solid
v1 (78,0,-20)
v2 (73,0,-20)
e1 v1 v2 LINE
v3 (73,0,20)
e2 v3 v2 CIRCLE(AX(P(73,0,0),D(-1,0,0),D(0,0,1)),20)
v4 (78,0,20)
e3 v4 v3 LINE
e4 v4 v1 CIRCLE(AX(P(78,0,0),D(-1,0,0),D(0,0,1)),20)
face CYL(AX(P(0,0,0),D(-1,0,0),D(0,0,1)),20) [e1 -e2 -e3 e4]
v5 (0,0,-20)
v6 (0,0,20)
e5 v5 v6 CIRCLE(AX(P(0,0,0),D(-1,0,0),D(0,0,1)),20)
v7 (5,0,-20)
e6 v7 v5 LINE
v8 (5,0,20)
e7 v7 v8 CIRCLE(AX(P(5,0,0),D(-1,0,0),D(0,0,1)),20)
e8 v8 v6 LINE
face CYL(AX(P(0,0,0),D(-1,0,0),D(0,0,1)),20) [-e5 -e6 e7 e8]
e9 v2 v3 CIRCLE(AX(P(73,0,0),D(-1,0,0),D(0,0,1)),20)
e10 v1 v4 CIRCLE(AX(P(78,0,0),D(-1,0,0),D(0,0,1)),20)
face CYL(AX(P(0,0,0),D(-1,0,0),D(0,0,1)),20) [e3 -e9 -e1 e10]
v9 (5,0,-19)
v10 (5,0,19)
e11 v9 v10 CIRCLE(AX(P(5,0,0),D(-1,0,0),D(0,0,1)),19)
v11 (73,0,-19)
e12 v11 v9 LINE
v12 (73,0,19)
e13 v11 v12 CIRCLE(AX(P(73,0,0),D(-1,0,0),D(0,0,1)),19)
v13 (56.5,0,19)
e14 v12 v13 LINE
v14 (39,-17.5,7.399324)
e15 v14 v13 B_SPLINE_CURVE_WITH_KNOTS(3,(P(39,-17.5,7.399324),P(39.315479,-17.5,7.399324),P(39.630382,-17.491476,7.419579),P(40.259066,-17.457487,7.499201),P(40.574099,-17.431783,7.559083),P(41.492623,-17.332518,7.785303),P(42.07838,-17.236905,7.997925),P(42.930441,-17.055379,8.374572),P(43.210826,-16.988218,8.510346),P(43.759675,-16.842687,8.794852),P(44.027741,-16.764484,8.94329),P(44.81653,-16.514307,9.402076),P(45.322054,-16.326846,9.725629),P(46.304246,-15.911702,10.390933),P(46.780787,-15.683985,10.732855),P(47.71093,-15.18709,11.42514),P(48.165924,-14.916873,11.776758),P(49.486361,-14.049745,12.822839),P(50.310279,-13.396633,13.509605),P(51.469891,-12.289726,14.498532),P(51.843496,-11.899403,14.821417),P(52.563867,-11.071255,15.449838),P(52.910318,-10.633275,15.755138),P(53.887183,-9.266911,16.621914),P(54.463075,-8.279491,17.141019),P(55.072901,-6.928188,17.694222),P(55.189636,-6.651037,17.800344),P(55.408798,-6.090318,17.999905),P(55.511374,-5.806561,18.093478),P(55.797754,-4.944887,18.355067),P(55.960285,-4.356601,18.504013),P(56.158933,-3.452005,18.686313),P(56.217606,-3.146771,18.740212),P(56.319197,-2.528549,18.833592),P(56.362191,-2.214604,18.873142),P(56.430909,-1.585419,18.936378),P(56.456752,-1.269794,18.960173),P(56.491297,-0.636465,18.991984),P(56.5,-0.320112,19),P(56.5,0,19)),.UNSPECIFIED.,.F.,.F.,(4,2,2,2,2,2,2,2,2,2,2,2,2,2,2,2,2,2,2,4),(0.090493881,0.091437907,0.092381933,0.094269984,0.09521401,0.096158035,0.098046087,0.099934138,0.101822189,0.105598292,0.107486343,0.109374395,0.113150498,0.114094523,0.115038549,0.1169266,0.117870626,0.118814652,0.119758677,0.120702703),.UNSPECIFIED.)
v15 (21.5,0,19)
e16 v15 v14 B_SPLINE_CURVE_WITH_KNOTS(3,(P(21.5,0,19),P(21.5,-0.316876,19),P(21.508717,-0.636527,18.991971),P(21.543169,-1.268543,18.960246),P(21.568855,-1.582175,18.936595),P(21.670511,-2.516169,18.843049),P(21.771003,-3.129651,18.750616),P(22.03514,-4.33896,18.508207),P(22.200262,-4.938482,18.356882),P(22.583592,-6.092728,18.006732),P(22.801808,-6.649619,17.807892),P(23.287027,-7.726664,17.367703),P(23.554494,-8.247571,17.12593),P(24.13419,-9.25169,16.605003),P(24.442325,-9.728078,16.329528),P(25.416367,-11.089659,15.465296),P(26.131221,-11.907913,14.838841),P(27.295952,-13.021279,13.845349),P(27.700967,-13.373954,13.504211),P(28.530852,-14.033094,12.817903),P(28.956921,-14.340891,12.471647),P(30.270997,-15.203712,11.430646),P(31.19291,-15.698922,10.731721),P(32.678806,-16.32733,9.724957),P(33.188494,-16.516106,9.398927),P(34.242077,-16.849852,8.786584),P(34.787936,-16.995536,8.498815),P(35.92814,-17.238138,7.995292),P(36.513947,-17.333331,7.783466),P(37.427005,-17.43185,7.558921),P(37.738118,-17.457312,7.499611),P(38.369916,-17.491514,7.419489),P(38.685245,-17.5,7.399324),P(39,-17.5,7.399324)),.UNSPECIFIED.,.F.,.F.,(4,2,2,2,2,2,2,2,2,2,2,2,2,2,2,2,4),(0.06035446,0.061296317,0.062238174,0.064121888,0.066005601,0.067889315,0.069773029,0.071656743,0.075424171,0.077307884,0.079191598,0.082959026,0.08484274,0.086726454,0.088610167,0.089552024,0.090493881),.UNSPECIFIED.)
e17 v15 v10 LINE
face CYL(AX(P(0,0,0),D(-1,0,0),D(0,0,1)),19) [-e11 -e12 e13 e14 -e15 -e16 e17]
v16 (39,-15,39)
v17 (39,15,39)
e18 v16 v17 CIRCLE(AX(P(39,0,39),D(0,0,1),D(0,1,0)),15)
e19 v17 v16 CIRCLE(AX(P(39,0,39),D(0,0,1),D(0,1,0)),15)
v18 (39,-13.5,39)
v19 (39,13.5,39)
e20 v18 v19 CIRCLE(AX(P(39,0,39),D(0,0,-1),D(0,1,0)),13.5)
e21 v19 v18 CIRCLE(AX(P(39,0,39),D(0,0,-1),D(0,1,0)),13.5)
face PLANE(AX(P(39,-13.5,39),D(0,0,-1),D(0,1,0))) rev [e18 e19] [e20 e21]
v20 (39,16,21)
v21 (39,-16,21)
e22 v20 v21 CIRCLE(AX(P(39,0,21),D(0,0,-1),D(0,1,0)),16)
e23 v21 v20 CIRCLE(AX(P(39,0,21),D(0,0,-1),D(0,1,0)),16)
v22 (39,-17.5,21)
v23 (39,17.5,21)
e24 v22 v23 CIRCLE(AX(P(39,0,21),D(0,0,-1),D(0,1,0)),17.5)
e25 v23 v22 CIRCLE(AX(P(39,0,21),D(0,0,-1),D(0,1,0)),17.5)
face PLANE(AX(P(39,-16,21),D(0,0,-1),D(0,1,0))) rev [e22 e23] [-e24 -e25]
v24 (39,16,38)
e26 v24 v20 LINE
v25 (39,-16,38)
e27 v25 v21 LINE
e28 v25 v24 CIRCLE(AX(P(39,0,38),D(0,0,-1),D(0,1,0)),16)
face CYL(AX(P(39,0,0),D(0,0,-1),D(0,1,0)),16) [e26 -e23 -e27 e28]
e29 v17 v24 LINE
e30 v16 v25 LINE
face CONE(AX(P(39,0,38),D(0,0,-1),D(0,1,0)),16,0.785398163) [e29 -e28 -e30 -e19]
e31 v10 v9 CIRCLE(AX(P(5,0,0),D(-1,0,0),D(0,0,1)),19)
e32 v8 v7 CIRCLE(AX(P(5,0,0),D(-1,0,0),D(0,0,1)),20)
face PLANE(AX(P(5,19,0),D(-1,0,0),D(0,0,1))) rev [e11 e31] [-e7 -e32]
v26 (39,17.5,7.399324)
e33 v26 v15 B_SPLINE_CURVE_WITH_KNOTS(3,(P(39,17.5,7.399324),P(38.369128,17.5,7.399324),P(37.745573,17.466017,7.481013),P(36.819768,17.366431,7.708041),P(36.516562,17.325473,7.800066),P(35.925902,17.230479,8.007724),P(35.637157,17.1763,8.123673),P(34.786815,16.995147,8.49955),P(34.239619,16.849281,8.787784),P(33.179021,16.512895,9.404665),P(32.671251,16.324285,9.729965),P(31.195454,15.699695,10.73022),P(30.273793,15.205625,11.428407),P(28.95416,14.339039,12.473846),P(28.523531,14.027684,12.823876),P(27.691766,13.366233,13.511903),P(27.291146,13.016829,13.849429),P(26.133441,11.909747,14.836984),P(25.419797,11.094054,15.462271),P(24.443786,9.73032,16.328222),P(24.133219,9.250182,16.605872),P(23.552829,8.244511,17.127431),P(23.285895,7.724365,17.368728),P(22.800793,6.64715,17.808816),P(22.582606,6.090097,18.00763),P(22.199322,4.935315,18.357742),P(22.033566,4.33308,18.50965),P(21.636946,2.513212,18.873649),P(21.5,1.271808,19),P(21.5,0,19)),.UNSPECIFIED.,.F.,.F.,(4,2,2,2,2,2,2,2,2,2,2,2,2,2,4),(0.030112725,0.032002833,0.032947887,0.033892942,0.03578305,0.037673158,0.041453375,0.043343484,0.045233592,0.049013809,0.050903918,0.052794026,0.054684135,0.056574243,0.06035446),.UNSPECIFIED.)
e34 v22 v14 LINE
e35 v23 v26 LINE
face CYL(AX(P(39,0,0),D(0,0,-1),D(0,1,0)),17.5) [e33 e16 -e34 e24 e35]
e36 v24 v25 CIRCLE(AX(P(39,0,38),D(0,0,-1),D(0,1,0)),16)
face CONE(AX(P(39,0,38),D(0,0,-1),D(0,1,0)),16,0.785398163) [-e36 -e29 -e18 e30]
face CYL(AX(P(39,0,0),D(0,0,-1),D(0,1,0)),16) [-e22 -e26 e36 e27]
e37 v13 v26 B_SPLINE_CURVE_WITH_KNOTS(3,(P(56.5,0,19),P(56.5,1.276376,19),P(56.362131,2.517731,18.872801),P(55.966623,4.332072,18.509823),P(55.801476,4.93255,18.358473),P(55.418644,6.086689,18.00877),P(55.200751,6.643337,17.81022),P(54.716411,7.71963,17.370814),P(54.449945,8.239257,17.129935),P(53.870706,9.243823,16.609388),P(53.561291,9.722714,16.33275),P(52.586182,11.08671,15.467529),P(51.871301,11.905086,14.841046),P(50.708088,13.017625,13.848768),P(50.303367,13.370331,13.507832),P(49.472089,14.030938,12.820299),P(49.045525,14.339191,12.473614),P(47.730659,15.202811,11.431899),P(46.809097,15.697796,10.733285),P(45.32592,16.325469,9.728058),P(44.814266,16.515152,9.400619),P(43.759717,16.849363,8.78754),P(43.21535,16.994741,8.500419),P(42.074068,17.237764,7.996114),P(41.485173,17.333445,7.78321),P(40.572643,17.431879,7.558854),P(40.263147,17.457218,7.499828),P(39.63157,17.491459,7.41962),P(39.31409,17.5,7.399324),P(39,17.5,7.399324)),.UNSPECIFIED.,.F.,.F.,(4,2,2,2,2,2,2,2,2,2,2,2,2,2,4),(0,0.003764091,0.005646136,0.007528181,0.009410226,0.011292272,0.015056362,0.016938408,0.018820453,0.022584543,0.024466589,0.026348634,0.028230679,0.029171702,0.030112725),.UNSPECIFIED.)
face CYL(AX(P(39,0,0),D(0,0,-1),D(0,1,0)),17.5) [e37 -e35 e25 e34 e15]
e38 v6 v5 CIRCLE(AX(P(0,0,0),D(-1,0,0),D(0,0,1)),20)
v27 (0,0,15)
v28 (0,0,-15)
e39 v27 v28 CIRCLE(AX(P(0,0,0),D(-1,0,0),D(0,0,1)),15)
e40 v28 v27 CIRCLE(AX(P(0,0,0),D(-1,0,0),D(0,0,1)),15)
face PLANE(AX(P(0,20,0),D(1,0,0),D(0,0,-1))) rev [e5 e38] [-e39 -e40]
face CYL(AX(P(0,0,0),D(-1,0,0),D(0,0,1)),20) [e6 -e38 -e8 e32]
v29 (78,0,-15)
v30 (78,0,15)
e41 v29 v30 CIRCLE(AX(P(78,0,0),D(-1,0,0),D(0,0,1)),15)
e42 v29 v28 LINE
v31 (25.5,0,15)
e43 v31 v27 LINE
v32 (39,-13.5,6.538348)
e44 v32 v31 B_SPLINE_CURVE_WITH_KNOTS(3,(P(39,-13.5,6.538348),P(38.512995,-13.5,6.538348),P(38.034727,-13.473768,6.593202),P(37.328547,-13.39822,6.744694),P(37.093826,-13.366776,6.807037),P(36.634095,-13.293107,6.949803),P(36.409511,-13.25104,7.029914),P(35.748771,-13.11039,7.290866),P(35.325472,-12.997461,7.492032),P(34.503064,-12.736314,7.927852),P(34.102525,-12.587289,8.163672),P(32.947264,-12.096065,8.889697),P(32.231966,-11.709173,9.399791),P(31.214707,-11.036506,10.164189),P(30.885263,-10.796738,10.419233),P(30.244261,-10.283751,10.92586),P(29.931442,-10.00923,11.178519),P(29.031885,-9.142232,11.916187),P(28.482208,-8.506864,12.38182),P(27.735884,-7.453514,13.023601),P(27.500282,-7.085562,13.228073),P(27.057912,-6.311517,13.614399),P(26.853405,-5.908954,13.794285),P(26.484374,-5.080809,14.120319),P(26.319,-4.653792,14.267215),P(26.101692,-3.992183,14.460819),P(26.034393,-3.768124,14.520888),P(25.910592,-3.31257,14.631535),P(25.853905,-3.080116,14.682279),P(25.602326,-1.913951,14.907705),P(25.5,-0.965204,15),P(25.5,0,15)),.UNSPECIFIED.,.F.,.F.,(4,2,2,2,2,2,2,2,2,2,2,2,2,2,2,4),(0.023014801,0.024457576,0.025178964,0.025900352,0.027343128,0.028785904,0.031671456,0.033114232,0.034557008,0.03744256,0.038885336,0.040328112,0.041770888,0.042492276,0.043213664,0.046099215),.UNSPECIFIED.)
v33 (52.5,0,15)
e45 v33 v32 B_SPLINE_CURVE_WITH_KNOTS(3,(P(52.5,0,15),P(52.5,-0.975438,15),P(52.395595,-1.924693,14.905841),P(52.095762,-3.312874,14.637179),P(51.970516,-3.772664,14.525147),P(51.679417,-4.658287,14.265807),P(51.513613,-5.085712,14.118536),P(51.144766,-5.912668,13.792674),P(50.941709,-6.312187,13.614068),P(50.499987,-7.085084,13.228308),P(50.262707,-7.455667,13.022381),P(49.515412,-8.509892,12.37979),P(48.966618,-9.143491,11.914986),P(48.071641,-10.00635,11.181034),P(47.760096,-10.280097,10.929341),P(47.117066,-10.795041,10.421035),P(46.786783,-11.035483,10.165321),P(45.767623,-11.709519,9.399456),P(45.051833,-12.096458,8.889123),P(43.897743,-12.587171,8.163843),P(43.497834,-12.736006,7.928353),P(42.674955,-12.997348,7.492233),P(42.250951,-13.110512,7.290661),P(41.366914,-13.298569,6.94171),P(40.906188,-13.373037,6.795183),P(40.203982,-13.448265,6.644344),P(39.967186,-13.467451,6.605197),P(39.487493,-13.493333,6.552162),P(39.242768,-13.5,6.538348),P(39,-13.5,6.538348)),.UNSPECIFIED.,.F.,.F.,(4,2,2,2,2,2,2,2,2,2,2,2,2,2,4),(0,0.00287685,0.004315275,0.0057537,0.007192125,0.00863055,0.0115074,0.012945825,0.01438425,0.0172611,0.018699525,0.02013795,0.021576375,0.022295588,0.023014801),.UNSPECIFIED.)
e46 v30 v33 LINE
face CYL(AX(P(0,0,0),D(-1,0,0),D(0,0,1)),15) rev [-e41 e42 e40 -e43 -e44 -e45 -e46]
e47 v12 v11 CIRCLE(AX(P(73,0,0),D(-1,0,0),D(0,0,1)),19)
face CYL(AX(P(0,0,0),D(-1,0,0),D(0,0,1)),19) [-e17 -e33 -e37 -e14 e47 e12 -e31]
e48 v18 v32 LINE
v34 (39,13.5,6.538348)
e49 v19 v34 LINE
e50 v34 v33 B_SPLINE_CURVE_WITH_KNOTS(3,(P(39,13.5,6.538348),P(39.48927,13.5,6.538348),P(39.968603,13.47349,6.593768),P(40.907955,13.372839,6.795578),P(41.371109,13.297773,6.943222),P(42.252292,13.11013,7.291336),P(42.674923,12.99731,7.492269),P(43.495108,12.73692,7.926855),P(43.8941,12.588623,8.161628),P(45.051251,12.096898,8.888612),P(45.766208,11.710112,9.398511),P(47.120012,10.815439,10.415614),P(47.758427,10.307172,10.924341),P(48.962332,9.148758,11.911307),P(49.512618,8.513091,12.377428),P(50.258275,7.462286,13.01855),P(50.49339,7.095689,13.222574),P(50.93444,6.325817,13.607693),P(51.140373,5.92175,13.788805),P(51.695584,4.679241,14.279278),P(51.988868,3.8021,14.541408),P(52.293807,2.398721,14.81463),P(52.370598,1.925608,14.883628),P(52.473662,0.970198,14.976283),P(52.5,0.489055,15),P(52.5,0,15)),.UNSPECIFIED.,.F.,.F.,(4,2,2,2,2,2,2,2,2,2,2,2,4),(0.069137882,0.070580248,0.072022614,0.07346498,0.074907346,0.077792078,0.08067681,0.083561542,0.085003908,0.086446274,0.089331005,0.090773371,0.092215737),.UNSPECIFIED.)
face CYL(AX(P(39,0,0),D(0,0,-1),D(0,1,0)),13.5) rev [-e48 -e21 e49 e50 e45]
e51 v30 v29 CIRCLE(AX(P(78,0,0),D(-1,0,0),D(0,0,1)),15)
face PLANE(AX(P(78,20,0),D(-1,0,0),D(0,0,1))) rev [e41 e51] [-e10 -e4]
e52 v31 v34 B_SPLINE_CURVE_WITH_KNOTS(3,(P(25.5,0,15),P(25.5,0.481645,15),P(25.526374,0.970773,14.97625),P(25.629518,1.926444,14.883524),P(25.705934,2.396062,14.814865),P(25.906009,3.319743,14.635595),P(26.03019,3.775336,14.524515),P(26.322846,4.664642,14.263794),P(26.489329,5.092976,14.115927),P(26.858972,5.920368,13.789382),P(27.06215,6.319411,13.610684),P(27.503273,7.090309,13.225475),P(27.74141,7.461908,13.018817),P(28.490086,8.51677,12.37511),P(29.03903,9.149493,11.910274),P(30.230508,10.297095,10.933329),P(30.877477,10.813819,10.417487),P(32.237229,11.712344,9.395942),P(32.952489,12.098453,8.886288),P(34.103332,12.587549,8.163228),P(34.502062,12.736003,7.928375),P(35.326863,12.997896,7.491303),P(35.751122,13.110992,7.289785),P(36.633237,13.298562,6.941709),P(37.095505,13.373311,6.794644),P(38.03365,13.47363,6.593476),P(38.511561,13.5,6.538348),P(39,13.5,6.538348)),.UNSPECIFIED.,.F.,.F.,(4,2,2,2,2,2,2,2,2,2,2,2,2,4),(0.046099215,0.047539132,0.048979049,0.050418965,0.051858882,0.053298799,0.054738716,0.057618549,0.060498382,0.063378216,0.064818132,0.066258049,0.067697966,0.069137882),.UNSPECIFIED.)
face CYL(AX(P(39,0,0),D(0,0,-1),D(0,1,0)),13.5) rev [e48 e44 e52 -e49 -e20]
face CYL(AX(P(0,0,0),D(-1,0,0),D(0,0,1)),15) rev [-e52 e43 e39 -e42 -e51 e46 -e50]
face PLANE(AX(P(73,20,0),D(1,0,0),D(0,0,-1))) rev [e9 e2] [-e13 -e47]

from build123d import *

# Parameters (mm, degrees)
SKETCH4_R          = 15
CUT_EXTRUDE1_DEPTH = 90.470665715
CUT_EXTRUDE2_REACH = 101.825
SKETCH5_R          = 13.5
CHAMFER1_SIZE      = 1


with BuildPart() as part:
    # Sketch1 → Revolve1 (revolve)
    with BuildSketch(Plane.XY, mode=Mode.PRIVATE) as revolve1_sk:
        Polygon((5, 19), (5, 20), (0, 20), (0, 15), (78, 15), (78, 20), (73, 20), (73, 19), align=None)
    revolve(revolve1_sk.sketch.rotate(Axis((0, 0, 0), (1, 0, 0)), 90), axis=Axis((0, 0, 0), (1, 0, 0)))

    # Sketch3 → Revolve2 (revolve)
    with BuildSketch(Plane(origin=(39, 0, 0), x_dir=(0, 0, -1), z_dir=(1, 0, 0)), mode=Mode.PRIVATE) as revolve2_sk:
        Polygon((-39, -13.5), (-39, -16), (-21, -16), (-21, -17.5), (-6.538348415, -17.5), (-6.538348415, -13.5), align=None)
    revolve(revolve2_sk.sketch.rotate(Axis((39, 0, 0), (0, 0, 1)), 180), axis=Axis((39, 0, 0), (0, 0, 1)))

    # Sketch4 → Cut-Extrude1 (cut, through all)
    with BuildSketch(Plane.ZY):
        Circle(SKETCH4_R)
    extrude(amount=-CUT_EXTRUDE1_DEPTH, mode=Mode.SUBTRACT)

    # Sketch5 → Cut-Extrude2 (cut, up to next)
    with BuildSketch(Plane.XY.offset(39), mode=Mode.PRIVATE) as cut_extrude2_sk1:
        with Locations(Location((39, 0, 0), (0, 0, 90))):
            Circle(SKETCH5_R)
    cut_extrude2_tool1 = extrude(cut_extrude2_sk1.sketch, amount=-CUT_EXTRUDE2_REACH, mode=Mode.PRIVATE) & part.part
    add(cut_extrude2_tool1.solids().sort_by_distance((39, 0, 39))[0], mode=Mode.SUBTRACT)

    # Chamfer1
    chamfer1_edges = [part.edges().sort_by_distance(p)[0] for p in [
        (39, -16, 39),
    ]]
    chamfer(chamfer1_edges, length=CHAMFER1_SIZE)


solid = part.part
